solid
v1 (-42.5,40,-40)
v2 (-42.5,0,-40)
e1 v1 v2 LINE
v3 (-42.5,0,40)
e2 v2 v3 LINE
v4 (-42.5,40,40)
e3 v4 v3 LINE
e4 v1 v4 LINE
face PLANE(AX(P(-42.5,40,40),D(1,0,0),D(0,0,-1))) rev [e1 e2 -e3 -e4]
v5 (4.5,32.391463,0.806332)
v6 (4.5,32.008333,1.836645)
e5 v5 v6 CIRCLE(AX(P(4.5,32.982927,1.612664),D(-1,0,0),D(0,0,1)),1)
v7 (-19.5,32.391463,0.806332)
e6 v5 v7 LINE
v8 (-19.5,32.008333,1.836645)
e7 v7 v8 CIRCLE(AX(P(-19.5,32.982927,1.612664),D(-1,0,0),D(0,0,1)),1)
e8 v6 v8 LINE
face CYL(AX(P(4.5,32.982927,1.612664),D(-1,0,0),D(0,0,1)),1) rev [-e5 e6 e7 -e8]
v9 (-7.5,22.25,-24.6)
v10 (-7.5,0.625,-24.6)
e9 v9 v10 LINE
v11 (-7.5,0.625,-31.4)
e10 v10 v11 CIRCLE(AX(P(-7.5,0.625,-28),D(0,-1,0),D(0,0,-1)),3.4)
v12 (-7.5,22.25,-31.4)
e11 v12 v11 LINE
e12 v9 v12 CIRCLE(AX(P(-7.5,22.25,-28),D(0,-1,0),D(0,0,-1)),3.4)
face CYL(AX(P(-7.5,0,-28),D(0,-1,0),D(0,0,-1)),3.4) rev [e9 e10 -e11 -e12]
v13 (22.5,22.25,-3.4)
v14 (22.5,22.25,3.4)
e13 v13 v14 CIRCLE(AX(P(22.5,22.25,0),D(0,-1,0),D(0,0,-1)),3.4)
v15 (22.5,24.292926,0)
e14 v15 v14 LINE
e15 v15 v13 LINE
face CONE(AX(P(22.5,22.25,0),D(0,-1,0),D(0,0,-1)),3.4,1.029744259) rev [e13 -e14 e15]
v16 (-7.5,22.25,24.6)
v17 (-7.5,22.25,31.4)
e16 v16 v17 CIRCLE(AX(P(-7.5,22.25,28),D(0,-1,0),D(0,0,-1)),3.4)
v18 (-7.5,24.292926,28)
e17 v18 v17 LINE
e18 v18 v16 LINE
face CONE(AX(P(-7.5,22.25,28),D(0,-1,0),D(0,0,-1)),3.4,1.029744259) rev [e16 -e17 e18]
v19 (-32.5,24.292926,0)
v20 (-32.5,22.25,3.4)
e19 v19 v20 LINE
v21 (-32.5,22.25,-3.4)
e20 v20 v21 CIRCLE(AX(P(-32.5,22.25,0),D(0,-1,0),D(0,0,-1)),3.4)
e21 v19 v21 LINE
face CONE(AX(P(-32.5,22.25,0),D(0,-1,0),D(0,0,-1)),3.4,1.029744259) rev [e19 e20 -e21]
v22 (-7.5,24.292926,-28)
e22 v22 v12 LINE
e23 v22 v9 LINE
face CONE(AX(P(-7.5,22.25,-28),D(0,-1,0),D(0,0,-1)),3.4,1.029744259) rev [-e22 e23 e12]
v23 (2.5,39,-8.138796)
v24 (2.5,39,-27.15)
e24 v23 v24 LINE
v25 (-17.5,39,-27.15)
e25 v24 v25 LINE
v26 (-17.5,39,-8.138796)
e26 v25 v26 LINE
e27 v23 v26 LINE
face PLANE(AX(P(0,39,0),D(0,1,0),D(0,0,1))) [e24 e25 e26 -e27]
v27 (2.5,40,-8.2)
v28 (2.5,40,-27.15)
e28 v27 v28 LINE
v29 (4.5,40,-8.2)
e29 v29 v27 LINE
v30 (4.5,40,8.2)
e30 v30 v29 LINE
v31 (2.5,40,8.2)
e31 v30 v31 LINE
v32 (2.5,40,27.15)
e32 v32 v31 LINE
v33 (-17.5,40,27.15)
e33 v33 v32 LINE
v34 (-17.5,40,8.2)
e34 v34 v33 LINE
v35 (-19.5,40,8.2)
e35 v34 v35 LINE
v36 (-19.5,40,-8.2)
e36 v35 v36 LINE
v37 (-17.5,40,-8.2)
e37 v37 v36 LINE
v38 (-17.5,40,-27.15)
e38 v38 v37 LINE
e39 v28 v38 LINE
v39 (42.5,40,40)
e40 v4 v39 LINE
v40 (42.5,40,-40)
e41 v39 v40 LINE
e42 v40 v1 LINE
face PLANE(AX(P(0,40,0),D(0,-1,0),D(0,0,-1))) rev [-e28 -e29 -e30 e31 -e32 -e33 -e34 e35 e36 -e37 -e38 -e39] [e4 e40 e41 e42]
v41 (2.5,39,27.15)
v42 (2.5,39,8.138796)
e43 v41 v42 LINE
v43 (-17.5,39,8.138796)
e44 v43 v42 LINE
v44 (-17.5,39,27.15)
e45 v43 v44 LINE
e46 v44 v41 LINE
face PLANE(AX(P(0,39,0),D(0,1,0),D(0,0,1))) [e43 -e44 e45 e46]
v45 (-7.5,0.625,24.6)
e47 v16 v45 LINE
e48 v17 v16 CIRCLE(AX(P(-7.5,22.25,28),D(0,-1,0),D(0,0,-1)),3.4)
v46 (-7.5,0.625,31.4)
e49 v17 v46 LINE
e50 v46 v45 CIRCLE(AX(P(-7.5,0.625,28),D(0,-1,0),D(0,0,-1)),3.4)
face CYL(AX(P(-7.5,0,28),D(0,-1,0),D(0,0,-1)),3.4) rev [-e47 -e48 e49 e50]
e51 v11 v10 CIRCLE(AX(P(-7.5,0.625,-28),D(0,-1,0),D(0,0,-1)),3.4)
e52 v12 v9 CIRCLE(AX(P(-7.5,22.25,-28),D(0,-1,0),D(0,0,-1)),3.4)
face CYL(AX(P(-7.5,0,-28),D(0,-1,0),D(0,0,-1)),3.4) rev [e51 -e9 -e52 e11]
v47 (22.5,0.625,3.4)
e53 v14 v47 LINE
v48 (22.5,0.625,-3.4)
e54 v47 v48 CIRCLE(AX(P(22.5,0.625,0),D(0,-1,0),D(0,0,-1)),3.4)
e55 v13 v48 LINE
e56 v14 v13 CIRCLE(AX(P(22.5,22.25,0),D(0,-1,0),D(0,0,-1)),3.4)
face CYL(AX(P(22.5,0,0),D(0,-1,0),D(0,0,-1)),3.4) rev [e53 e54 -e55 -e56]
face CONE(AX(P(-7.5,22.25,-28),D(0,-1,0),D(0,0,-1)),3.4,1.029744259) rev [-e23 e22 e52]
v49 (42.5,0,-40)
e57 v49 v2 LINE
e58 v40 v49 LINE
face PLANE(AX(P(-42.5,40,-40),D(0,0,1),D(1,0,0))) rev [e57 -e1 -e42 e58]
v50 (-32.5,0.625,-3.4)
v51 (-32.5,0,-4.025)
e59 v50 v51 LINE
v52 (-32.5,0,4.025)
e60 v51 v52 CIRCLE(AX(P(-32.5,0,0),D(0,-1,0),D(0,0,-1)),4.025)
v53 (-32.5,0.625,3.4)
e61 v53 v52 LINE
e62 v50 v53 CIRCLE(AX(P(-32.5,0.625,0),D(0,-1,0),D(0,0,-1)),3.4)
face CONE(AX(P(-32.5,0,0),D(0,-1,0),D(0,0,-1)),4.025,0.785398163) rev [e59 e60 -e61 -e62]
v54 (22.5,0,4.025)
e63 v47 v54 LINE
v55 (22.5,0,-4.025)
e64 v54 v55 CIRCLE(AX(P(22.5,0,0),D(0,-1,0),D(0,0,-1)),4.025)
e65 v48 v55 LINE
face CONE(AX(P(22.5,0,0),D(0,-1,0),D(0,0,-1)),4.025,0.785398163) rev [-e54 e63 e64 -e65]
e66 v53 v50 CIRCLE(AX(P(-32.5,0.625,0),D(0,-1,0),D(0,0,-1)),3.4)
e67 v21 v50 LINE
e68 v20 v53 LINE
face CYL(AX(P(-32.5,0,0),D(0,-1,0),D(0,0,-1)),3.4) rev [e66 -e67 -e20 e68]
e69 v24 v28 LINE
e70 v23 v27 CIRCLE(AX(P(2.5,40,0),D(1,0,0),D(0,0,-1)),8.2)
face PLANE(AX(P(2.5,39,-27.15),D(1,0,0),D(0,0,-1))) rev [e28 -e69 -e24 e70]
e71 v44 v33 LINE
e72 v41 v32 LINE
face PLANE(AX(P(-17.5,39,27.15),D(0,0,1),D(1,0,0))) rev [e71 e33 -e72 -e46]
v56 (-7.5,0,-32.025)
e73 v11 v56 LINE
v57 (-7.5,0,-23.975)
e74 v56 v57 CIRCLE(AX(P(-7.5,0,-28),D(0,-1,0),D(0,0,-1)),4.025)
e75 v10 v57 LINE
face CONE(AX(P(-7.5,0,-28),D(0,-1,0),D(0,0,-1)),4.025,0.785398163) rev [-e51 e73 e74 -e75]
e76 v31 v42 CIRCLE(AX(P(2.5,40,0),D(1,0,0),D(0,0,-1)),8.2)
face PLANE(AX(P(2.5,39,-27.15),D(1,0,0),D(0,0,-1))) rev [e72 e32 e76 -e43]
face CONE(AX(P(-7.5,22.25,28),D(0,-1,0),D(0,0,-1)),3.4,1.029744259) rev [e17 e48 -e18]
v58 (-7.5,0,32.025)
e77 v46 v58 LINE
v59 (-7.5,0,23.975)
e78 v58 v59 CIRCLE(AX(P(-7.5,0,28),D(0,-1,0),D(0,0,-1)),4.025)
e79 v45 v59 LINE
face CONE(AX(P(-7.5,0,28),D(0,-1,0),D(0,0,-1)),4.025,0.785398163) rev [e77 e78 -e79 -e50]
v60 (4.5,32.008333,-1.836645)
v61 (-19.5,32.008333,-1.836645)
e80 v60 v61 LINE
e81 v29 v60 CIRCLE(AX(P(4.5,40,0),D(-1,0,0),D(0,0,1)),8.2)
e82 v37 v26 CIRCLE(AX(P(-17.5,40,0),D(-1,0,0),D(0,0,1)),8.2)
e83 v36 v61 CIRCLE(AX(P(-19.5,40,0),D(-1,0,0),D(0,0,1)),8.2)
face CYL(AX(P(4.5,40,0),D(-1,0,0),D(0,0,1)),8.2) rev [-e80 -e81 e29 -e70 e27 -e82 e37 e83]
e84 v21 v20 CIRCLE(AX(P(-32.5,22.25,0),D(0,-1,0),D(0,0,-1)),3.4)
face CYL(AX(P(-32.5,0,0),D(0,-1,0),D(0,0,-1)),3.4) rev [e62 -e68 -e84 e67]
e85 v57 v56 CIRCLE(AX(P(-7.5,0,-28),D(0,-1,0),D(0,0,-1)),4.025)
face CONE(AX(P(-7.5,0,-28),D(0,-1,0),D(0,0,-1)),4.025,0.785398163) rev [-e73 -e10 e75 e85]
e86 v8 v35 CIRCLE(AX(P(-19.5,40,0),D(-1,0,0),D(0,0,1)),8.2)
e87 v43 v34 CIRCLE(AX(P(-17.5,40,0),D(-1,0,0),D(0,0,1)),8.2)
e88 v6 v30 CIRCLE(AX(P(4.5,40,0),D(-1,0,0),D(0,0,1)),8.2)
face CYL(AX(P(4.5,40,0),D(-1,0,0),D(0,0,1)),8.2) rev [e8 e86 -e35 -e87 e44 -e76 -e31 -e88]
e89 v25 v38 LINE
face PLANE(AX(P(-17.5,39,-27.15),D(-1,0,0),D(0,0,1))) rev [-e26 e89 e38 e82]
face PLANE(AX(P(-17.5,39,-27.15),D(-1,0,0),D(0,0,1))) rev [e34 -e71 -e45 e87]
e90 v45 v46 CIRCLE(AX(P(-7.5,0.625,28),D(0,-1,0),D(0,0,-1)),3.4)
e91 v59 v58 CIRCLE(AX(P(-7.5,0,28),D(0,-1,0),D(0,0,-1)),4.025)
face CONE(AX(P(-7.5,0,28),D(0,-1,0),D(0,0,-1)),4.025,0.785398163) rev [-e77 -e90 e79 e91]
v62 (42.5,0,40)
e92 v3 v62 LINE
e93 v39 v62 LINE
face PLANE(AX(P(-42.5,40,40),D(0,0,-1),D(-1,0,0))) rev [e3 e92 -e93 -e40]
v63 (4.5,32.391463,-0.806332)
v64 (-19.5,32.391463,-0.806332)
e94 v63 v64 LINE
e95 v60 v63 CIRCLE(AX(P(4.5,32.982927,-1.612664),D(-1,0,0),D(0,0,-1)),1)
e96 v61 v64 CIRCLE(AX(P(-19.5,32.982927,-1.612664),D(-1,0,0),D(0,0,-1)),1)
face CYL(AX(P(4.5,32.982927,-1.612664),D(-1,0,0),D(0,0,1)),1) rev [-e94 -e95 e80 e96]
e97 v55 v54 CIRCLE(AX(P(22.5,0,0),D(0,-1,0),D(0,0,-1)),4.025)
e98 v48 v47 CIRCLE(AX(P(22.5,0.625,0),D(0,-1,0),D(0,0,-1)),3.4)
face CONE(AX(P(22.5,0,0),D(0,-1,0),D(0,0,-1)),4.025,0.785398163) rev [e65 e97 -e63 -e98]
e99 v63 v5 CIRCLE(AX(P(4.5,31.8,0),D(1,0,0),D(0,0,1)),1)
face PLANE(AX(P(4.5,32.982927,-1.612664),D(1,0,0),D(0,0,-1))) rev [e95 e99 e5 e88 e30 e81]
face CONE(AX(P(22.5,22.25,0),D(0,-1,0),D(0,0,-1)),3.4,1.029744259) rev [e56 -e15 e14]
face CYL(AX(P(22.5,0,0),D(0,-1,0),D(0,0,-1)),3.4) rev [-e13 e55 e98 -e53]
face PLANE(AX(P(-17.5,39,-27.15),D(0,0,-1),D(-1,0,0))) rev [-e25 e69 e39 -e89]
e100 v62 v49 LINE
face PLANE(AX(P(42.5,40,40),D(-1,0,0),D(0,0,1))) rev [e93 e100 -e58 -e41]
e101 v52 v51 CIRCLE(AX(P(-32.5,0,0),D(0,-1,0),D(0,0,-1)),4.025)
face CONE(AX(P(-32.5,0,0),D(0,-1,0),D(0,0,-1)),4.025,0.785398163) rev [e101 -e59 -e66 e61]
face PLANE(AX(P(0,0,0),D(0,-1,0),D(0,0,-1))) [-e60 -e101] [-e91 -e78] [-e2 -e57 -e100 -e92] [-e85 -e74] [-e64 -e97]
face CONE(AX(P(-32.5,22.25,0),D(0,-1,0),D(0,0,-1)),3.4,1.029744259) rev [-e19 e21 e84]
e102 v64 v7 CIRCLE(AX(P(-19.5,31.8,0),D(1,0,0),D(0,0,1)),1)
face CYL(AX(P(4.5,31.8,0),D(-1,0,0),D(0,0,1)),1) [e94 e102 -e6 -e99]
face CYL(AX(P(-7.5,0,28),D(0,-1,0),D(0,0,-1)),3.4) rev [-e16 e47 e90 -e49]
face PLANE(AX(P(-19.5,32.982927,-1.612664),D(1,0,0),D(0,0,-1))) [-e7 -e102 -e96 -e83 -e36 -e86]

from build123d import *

# Parameters (mm, degrees)
SKETCH1_W                   = 85
SKETCH1_H                   = 80
BOSS_EXTRUDE1_DEPTH         = 40
M8_TAPPED_HOLE1_D           = 6.8
M8_TAPPED_HOLE1_DEPTH       = 22.25
M8_TAPPED_HOLE1_CSINK_D     = 8.05
M8_TAPPED_HOLE1_CSINK_ANGLE = 90
M8_TAPPED_HOLE1_TIP         = 2.042926105
SKETCH5_W                   = 20
SKETCH5_H                   = 54.3
CUT_EXTRUDE1_DEPTH          = 1
CUT_EXTRUDE2_DEPTH          = 12


with BuildPart() as part:
    # Sketch1 → Boss-Extrude1 (new body)
    with BuildSketch(Plane(origin=(0, 0, 0), x_dir=(1, 0, 0), z_dir=(0, 1, 0))):
        Rectangle(SKETCH1_W, SKETCH1_H)
    extrude(amount=BOSS_EXTRUDE1_DEPTH)

    # M8 Tapped Hole1
    with Locations(Plane(origin=(0, 0, 0), x_dir=(-1, 0, 0), z_dir=(0, -1, 0))):
        with Locations((7.5, 28), (-22.5, 0), (7.5, -28), (32.5, 0)):
            CounterSinkHole(M8_TAPPED_HOLE1_D / 2, M8_TAPPED_HOLE1_CSINK_D / 2, depth=M8_TAPPED_HOLE1_DEPTH, counter_sink_angle=M8_TAPPED_HOLE1_CSINK_ANGLE)
            with Locations((0, 0, -(M8_TAPPED_HOLE1_DEPTH + M8_TAPPED_HOLE1_TIP / 2))):  # 118° drill point
                Cone(0, M8_TAPPED_HOLE1_D / 2, M8_TAPPED_HOLE1_TIP, mode=Mode.SUBTRACT)

    # Sketch5 → Cut-Extrude1 (cut)
    with BuildSketch(Plane(origin=(0, 40, 0), x_dir=(1, 0, 0), z_dir=(0, 1, 0))):
        with Locations((-7.5, 0)):
            Rectangle(SKETCH5_W, SKETCH5_H)
    extrude(amount=-CUT_EXTRUDE1_DEPTH, mode=Mode.SUBTRACT)

    # Sketch6 → Cut-Extrude2 (cut, symmetric)
    with BuildSketch(Plane.ZY.offset(7.5)):
        with BuildLine():
            Line((-8.2, 40), (8.2, 40))
            ThreePointArc((8.2, 40), (6.414845549, 34.892186713), (1.836644737, 32.008333333))
            ThreePointArc((1.836644737, 32.008333333), (1.264123473, 32.045632996), (0.806331836, 32.391463415))
            ThreePointArc((0.806331836, 32.391463415), (0, 32.8), (-0.806331836, 32.391463415))
            ThreePointArc((-0.806331836, 32.391463415), (-1.264123473, 32.045632996), (-1.836644737, 32.008333333))
            ThreePointArc((-1.836644737, 32.008333333), (-6.414845549, 34.892186713), (-8.2, 40))
        make_face()
    extrude(amount=CUT_EXTRUDE2_DEPTH, both=True, mode=Mode.SUBTRACT)


solid = part.part
